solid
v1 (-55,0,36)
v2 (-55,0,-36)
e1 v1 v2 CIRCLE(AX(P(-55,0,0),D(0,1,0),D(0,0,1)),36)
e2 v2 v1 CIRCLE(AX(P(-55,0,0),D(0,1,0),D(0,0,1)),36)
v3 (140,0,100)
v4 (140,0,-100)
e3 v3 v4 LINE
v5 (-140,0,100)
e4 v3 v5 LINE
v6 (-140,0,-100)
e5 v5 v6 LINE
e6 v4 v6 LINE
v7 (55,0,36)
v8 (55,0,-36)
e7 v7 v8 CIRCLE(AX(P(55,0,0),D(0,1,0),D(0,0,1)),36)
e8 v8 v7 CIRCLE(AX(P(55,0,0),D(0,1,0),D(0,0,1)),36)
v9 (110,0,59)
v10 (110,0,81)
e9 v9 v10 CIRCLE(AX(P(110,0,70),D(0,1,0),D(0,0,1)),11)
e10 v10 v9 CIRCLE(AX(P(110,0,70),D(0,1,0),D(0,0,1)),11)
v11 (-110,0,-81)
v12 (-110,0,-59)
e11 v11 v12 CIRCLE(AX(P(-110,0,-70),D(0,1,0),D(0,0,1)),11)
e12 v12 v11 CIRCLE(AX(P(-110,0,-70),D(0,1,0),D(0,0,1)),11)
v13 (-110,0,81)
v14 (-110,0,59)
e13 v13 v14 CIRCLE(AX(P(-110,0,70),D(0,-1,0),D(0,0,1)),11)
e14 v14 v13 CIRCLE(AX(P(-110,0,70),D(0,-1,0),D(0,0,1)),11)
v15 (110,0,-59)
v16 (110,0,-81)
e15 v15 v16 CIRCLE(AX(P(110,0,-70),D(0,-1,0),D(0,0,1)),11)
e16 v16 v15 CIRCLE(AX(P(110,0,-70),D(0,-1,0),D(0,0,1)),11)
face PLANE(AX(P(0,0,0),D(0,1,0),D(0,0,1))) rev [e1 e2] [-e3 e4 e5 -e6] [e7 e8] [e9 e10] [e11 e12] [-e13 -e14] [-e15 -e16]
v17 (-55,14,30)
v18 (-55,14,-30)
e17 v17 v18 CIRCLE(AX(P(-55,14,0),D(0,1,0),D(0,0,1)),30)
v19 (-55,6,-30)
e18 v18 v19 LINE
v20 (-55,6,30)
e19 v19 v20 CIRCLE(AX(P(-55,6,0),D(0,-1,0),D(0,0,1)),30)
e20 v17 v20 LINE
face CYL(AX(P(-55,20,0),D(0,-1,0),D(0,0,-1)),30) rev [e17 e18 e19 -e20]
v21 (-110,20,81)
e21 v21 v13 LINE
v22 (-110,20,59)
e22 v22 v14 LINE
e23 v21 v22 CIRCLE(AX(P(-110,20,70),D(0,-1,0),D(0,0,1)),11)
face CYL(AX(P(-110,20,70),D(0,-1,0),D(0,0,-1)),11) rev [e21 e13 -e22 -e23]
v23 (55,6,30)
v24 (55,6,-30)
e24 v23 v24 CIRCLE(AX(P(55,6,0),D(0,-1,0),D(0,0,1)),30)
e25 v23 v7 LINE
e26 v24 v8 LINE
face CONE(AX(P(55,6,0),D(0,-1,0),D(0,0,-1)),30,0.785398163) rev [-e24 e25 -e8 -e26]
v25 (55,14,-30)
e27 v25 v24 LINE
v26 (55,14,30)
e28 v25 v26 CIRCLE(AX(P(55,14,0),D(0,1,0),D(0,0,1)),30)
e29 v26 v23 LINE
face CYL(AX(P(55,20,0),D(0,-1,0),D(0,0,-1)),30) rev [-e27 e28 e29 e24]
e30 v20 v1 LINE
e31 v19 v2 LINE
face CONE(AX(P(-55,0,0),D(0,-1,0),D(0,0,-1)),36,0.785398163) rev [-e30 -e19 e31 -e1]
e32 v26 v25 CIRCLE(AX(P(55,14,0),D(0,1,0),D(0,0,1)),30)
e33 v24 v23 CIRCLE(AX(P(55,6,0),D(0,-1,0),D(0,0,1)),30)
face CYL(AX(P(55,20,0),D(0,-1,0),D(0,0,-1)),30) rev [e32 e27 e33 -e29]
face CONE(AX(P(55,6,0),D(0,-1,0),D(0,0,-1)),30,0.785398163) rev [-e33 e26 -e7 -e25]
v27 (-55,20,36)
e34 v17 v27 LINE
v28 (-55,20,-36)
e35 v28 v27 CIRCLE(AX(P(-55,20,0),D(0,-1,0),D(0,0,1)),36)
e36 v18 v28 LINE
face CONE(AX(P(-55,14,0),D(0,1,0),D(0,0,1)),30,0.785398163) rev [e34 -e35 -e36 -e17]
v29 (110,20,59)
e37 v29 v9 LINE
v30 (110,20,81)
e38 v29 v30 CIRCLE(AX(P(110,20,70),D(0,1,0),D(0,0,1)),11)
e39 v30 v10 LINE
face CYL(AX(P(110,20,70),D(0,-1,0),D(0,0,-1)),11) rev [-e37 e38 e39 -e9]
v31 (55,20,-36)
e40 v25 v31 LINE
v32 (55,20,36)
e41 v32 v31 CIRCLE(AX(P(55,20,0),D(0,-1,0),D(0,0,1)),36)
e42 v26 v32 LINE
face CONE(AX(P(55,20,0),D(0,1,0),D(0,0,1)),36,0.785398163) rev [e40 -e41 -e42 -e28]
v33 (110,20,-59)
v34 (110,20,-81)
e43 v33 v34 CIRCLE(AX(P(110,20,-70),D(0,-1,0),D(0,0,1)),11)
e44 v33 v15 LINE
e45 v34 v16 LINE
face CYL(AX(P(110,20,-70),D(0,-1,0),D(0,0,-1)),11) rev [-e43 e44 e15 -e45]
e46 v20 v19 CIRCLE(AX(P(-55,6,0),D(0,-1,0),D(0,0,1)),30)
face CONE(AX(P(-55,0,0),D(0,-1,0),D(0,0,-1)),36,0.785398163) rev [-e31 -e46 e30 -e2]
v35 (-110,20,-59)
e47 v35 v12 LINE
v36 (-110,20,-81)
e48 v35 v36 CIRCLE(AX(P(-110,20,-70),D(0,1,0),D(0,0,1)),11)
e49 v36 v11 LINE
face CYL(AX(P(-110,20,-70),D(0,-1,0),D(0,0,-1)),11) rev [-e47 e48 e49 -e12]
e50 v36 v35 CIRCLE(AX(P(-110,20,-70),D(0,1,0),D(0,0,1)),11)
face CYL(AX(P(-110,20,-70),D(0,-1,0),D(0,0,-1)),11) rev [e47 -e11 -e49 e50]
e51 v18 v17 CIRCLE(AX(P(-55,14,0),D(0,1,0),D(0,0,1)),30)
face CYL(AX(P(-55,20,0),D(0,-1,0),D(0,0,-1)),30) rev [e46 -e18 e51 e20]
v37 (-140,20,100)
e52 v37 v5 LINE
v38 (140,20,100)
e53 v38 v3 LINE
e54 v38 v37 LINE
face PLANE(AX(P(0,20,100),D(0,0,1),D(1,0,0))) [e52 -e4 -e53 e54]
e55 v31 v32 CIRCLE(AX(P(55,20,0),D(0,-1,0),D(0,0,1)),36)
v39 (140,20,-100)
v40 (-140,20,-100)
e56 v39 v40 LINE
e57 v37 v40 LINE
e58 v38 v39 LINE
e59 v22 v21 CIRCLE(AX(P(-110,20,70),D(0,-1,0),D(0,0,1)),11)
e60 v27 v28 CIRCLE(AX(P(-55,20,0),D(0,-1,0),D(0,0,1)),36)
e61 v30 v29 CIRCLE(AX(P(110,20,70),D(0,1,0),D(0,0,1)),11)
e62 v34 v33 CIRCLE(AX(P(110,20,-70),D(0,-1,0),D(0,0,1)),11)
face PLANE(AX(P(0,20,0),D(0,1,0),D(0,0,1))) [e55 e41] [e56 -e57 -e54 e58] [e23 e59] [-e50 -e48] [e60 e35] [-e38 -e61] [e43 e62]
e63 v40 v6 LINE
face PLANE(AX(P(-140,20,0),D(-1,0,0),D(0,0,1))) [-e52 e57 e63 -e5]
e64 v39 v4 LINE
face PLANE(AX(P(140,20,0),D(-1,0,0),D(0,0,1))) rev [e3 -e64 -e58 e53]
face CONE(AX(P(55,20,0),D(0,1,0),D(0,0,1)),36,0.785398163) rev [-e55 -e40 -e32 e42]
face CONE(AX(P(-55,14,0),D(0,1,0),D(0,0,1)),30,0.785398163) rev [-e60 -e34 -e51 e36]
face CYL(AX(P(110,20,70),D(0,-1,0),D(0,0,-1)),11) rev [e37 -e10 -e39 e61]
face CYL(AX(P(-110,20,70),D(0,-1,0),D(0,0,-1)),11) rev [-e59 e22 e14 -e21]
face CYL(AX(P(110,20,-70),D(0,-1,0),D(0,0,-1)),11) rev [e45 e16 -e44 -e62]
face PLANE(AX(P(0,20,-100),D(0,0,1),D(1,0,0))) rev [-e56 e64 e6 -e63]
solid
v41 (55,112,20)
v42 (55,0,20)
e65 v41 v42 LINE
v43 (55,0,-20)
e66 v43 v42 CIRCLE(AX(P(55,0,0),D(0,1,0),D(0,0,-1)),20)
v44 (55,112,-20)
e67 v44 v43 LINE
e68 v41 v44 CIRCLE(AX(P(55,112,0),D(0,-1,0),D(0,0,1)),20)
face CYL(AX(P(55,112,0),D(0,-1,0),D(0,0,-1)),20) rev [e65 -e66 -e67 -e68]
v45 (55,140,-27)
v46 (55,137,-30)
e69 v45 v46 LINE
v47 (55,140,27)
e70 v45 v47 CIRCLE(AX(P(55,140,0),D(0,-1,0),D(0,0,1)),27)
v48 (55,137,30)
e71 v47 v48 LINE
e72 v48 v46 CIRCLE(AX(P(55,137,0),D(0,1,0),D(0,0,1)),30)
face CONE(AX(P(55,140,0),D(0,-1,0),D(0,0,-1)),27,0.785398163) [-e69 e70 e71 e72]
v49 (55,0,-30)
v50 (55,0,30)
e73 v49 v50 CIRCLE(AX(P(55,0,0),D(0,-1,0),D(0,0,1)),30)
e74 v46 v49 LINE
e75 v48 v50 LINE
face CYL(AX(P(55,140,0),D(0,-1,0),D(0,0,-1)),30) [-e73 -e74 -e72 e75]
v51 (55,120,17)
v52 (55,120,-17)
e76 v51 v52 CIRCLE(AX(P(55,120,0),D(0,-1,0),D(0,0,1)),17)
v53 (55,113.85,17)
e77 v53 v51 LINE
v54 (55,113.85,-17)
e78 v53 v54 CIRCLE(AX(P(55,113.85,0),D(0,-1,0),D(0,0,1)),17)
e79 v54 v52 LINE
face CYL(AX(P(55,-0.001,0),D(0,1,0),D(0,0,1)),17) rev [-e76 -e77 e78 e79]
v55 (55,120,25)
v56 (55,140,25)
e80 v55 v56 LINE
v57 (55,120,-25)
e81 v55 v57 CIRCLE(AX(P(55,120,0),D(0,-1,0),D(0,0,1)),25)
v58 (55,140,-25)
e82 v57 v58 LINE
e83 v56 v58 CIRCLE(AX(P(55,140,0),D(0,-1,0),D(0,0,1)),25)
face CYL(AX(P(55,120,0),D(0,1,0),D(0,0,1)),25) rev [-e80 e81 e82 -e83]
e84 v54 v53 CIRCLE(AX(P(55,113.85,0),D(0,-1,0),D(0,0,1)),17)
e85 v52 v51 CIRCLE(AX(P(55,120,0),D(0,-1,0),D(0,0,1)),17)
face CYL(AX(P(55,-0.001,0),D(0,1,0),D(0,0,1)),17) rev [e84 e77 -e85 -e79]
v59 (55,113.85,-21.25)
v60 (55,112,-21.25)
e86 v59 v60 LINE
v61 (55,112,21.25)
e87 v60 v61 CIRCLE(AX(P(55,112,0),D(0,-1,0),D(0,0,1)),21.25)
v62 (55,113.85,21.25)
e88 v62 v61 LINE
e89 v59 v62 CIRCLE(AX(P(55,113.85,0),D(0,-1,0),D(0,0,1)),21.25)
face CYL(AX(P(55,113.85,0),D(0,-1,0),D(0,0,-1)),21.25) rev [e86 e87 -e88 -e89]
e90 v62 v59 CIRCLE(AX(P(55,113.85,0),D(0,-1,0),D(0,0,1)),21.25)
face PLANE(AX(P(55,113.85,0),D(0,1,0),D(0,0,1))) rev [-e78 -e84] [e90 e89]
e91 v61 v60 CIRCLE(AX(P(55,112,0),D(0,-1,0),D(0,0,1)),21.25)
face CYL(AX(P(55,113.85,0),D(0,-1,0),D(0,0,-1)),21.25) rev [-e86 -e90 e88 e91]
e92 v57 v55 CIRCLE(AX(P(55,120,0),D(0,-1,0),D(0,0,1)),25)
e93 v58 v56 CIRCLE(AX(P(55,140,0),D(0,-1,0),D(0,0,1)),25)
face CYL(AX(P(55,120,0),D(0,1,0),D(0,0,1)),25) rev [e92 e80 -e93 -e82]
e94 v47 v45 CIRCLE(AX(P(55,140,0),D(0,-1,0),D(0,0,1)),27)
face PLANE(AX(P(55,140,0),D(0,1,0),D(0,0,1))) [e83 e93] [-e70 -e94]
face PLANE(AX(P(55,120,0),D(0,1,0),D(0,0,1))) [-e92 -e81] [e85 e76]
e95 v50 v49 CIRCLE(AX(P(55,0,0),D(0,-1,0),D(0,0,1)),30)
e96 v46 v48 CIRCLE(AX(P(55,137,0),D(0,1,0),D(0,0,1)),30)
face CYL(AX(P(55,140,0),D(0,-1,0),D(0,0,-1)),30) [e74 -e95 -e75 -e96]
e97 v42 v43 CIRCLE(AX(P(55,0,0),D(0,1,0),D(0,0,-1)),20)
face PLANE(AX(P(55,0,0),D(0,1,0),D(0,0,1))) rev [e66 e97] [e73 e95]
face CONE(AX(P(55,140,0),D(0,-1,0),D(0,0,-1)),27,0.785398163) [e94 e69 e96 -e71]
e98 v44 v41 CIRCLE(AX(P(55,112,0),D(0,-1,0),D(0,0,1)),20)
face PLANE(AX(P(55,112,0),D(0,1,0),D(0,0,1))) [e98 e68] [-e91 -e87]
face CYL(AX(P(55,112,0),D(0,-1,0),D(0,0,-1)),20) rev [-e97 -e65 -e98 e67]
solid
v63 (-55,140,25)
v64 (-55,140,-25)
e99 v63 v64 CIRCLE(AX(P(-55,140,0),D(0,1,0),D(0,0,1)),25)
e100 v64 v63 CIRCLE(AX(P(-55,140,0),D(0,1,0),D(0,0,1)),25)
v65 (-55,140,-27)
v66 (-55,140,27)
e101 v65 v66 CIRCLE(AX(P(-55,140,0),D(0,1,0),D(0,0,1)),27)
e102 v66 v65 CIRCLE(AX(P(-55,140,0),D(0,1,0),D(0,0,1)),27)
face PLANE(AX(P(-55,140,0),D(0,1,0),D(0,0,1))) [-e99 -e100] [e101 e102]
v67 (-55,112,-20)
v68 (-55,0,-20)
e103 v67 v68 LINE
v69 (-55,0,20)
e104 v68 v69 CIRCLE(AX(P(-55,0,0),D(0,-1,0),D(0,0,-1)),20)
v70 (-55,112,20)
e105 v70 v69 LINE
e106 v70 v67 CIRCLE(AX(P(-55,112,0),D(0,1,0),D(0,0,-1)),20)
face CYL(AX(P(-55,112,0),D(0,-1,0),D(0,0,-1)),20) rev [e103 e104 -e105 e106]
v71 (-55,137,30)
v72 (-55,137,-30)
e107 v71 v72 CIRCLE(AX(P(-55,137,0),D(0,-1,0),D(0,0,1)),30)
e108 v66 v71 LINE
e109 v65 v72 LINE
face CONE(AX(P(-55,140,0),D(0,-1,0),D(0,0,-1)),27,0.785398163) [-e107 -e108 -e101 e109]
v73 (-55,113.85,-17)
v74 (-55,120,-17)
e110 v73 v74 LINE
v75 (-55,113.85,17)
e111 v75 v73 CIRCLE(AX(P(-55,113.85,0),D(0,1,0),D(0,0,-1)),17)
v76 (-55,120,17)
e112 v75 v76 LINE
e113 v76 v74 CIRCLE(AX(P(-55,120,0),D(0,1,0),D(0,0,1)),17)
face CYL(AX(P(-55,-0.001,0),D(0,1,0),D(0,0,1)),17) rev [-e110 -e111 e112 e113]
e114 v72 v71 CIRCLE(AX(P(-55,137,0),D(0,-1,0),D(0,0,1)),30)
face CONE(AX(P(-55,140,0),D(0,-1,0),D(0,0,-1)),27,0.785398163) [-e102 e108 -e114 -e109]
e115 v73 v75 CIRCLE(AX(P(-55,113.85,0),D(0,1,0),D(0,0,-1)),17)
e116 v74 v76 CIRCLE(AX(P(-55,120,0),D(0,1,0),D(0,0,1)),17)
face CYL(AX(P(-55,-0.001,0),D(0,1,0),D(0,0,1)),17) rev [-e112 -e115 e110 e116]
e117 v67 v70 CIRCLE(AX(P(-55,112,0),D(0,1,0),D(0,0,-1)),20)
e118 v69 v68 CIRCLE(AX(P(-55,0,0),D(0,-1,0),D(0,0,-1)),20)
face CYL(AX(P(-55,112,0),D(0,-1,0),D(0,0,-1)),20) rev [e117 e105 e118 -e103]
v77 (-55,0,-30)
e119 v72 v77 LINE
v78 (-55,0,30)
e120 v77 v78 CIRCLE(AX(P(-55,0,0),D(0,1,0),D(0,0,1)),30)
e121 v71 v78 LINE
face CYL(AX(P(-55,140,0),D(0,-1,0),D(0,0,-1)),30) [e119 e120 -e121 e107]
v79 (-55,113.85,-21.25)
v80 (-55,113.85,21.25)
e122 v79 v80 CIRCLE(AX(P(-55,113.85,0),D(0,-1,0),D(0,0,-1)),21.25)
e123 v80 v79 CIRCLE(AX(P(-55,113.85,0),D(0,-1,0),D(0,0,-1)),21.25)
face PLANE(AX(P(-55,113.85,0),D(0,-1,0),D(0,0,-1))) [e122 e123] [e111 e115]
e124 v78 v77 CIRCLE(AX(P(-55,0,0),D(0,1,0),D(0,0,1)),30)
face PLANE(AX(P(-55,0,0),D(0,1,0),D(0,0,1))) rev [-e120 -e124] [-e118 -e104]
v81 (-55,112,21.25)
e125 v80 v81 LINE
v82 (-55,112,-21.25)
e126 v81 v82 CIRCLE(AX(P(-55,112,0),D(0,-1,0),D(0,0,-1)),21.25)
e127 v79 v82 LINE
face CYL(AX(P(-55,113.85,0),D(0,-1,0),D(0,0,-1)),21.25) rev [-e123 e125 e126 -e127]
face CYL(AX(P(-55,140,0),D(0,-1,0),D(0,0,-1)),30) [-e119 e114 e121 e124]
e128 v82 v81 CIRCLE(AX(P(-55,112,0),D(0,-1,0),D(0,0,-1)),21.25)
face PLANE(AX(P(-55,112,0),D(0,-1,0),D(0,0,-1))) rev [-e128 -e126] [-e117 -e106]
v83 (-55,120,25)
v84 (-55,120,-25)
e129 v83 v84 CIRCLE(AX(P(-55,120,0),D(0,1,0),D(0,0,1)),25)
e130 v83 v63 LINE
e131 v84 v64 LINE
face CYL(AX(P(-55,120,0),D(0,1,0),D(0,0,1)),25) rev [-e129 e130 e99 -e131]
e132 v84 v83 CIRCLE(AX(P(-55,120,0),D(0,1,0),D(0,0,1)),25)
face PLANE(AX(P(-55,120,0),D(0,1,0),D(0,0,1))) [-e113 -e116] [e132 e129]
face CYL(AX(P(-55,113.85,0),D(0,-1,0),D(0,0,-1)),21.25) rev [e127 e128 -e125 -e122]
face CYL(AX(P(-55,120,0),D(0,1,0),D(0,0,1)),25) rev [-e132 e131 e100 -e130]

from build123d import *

# Parameters (mm, degrees)
SKETCH_2_7_R        = 11
BOSS_EXTRUDE2_DEPTH = 20
CHAMFER1_SIZE       = 6
SKETCH_2_7_2_R      = 30
BOSS_EXTRUDE5_DEPTH = 140
SKETCH4_R           = 25
CUT_EXTRUDE2_DEPTH  = 20
SKETCH5_R           = 20
CUT_EXTRUDE3_DEPTH  = 112
SKETCH6_R           = 17
CUT_EXTRUDE4_DEPTH  = 8
CHAMFER2_SIZE       = 3
CUT_EXTRUDE5_START  = -112
SKETCH7_R           = 21.25
CUT_EXTRUDE5_DEPTH  = 1.85


with BuildPart() as part:
    # Sketch 2_7 → Boss-Extrude2 (new body)
    # profile 1 of 7: a face of its own
    with BuildSketch(Plane(origin=(0, 0, 0), x_dir=(1, 0, 0), z_dir=(0, 1, 0))):
        Polygon((-140, -100), (-85, -100), (-85, -4.73e-07), (-85, 100), (-140, 100), align=None)
        with Locations(Location((-110, -70, 0), (0, 0, 270))):
            Circle(SKETCH_2_7_R, mode=Mode.SUBTRACT)
        with Locations(Location((-110, 70, 0), (0, 0, 270))):
            Circle(SKETCH_2_7_R, mode=Mode.SUBTRACT)
    # profile 2 of 7: a face of its own
    with BuildSketch(Plane(origin=(0, 0, 0), x_dir=(1, 0, 0), z_dir=(0, 1, 0))):
        with BuildLine():
            Line((-85, -100), (-25, -100))
            Line((-25, -100), (-25, 0))
            ThreePointArc((-25, 0), (-54.999999763, -30), (-85, -4.73e-07))
            Line((-85, -4.73e-07), (-85, -100))
        make_face()
    # profile 3 of 7: a face of its own
    with BuildSketch(Plane(origin=(0, 0, 0), x_dir=(1, 0, 0), z_dir=(0, 1, 0))):
        with BuildLine():
            ThreePointArc((-85, -4.73e-07), (-55.000000237, 30), (-25, 0))
            Line((-25, 0), (-25, 100))
            Line((-25, 100), (-85, 100))
            Line((-85, 100), (-85, -4.73e-07))
        make_face()
    # profile 4 of 7: a face of its own
    with BuildSketch(Plane(origin=(0, 0, 0), x_dir=(1, 0, 0), z_dir=(0, 1, 0))):
        Polygon((-25, -100), (25, -100), (25, 5.4e-08), (25, 100), (-25, 100), (-25, 0), align=None)
    # profile 5 of 7: a face of its own
    with BuildSketch(Plane(origin=(0, 0, 0), x_dir=(1, 0, 0), z_dir=(0, 1, 0))):
        Polygon((85, -100), (140, -100), (140, 100), (85, 100), (85, 0), align=None)
        with Locations(Location((110, -70, 0), (0, 0, 270))):
            Circle(SKETCH_2_7_R, mode=Mode.SUBTRACT)
        with Locations(Location((110, 70, 0), (0, 0, 270))):
            Circle(SKETCH_2_7_R, mode=Mode.SUBTRACT)
    # profile 6 of 7: a face of its own
    with BuildSketch(Plane(origin=(0, 0, 0), x_dir=(1, 0, 0), z_dir=(0, 1, 0))):
        with BuildLine():
            ThreePointArc((25, 5.4e-08), (55.000000027, 30), (85, 0))
            Line((85, 0), (85, 100))
            Line((85, 100), (25, 100))
            Line((25, 100), (25, 5.4e-08))
        make_face()
    # profile 7 of 7: a face of its own
    with BuildSketch(Plane(origin=(0, 0, 0), x_dir=(1, 0, 0), z_dir=(0, 1, 0))):
        with BuildLine():
            Line((25, -100), (85, -100))
            Line((85, -100), (85, 0))
            ThreePointArc((85, 0), (54.999999973, -30), (25, 5.4e-08))
            Line((25, 5.4e-08), (25, -100))
        make_face()
    extrude(amount=BOSS_EXTRUDE2_DEPTH)

    # Chamfer1
    chamfer1_edges = [part.edges().sort_by_distance(p)[0] for p in [
        (-85, 0, 0),
        (85, 0, 5.4e-08),
        (85, 20, 5.4e-08),
        (-85, 20, 0),
    ]]
    chamfer(chamfer1_edges, length=CHAMFER1_SIZE)


with BuildPart() as body_2:
    # Sketch 2_7 2 → Boss-Extrude5 (new body)
    with BuildSketch(Plane(origin=(0, 0, 0), x_dir=(1, 0, 0), z_dir=(0, 1, 0))):
        with Locations(Location((-55, 0, 0), (0, 0, 270))):
            Circle(SKETCH_2_7_2_R)
    extrude(amount=BOSS_EXTRUDE5_DEPTH)

    # Sketch4 → Cut-Extrude2 (cut)
    with BuildSketch(Plane(origin=(0, 140, 0), x_dir=(1, 0, 0), z_dir=(0, 1, 0))):
        with Locations(Location((-55, 0, 0), (0, 0, 270))):
            Circle(SKETCH4_R)
    extrude(amount=-CUT_EXTRUDE2_DEPTH, mode=Mode.SUBTRACT)

    # Sketch5 → Cut-Extrude3 (cut)
    with BuildSketch(Plane.XZ):
        with Locations(Location((-55, 0, 0), (0, 0, 270))):
            Circle(SKETCH5_R)
    extrude(amount=-CUT_EXTRUDE3_DEPTH, mode=Mode.SUBTRACT)

    # Sketch6 → Cut-Extrude4 (cut)
    with BuildSketch(Plane(origin=(0, 120, 0), x_dir=(1, 0, 0), z_dir=(0, 1, 0))):
        with Locations(Location((-55, 0, 0), (0, 0, 270))):
            Circle(SKETCH6_R)
    extrude(amount=-CUT_EXTRUDE4_DEPTH, mode=Mode.SUBTRACT)

    # Chamfer2
    chamfer2_edges = [body_2.edges().sort_by_distance(p)[0] for p in [
        (-55, 140, -30),
    ]]
    chamfer(chamfer2_edges, length=CHAMFER2_SIZE)


with BuildPart() as body_3:
    # Mirror1: mirrored copy
    add(body_2.part.mirror(Plane(origin=(0, 0, 0), x_dir=(0, 0, 1), z_dir=(1, 0, 0))))


with BuildPart() as cut_extrude5_tool:
    # Sketch7 → Cut-Extrude5 (new body)
    with BuildSketch(Plane.XZ.offset(CUT_EXTRUDE5_START)):
        with Locations(Location((-55, 0, 0), (0, 0, 270))):
            Circle(SKETCH7_R)
        with Locations(Location((55, 0, 0), (0, 0, 90))):
            Circle(SKETCH7_R)
    extrude(amount=-CUT_EXTRUDE5_DEPTH)


with BuildPart() as body_2_1:
    add(body_2.part)

    # Cut-Extrude5: cut by cut_extrude5_tool
    add(cut_extrude5_tool.part, mode=Mode.SUBTRACT)


with BuildPart() as body_3_1:
    add(body_3.part)

    # Cut-Extrude5: cut by cut_extrude5_tool
    add(cut_extrude5_tool.part, mode=Mode.SUBTRACT)


solid = Compound([part.part, body_2_1.part, body_3_1.part])
